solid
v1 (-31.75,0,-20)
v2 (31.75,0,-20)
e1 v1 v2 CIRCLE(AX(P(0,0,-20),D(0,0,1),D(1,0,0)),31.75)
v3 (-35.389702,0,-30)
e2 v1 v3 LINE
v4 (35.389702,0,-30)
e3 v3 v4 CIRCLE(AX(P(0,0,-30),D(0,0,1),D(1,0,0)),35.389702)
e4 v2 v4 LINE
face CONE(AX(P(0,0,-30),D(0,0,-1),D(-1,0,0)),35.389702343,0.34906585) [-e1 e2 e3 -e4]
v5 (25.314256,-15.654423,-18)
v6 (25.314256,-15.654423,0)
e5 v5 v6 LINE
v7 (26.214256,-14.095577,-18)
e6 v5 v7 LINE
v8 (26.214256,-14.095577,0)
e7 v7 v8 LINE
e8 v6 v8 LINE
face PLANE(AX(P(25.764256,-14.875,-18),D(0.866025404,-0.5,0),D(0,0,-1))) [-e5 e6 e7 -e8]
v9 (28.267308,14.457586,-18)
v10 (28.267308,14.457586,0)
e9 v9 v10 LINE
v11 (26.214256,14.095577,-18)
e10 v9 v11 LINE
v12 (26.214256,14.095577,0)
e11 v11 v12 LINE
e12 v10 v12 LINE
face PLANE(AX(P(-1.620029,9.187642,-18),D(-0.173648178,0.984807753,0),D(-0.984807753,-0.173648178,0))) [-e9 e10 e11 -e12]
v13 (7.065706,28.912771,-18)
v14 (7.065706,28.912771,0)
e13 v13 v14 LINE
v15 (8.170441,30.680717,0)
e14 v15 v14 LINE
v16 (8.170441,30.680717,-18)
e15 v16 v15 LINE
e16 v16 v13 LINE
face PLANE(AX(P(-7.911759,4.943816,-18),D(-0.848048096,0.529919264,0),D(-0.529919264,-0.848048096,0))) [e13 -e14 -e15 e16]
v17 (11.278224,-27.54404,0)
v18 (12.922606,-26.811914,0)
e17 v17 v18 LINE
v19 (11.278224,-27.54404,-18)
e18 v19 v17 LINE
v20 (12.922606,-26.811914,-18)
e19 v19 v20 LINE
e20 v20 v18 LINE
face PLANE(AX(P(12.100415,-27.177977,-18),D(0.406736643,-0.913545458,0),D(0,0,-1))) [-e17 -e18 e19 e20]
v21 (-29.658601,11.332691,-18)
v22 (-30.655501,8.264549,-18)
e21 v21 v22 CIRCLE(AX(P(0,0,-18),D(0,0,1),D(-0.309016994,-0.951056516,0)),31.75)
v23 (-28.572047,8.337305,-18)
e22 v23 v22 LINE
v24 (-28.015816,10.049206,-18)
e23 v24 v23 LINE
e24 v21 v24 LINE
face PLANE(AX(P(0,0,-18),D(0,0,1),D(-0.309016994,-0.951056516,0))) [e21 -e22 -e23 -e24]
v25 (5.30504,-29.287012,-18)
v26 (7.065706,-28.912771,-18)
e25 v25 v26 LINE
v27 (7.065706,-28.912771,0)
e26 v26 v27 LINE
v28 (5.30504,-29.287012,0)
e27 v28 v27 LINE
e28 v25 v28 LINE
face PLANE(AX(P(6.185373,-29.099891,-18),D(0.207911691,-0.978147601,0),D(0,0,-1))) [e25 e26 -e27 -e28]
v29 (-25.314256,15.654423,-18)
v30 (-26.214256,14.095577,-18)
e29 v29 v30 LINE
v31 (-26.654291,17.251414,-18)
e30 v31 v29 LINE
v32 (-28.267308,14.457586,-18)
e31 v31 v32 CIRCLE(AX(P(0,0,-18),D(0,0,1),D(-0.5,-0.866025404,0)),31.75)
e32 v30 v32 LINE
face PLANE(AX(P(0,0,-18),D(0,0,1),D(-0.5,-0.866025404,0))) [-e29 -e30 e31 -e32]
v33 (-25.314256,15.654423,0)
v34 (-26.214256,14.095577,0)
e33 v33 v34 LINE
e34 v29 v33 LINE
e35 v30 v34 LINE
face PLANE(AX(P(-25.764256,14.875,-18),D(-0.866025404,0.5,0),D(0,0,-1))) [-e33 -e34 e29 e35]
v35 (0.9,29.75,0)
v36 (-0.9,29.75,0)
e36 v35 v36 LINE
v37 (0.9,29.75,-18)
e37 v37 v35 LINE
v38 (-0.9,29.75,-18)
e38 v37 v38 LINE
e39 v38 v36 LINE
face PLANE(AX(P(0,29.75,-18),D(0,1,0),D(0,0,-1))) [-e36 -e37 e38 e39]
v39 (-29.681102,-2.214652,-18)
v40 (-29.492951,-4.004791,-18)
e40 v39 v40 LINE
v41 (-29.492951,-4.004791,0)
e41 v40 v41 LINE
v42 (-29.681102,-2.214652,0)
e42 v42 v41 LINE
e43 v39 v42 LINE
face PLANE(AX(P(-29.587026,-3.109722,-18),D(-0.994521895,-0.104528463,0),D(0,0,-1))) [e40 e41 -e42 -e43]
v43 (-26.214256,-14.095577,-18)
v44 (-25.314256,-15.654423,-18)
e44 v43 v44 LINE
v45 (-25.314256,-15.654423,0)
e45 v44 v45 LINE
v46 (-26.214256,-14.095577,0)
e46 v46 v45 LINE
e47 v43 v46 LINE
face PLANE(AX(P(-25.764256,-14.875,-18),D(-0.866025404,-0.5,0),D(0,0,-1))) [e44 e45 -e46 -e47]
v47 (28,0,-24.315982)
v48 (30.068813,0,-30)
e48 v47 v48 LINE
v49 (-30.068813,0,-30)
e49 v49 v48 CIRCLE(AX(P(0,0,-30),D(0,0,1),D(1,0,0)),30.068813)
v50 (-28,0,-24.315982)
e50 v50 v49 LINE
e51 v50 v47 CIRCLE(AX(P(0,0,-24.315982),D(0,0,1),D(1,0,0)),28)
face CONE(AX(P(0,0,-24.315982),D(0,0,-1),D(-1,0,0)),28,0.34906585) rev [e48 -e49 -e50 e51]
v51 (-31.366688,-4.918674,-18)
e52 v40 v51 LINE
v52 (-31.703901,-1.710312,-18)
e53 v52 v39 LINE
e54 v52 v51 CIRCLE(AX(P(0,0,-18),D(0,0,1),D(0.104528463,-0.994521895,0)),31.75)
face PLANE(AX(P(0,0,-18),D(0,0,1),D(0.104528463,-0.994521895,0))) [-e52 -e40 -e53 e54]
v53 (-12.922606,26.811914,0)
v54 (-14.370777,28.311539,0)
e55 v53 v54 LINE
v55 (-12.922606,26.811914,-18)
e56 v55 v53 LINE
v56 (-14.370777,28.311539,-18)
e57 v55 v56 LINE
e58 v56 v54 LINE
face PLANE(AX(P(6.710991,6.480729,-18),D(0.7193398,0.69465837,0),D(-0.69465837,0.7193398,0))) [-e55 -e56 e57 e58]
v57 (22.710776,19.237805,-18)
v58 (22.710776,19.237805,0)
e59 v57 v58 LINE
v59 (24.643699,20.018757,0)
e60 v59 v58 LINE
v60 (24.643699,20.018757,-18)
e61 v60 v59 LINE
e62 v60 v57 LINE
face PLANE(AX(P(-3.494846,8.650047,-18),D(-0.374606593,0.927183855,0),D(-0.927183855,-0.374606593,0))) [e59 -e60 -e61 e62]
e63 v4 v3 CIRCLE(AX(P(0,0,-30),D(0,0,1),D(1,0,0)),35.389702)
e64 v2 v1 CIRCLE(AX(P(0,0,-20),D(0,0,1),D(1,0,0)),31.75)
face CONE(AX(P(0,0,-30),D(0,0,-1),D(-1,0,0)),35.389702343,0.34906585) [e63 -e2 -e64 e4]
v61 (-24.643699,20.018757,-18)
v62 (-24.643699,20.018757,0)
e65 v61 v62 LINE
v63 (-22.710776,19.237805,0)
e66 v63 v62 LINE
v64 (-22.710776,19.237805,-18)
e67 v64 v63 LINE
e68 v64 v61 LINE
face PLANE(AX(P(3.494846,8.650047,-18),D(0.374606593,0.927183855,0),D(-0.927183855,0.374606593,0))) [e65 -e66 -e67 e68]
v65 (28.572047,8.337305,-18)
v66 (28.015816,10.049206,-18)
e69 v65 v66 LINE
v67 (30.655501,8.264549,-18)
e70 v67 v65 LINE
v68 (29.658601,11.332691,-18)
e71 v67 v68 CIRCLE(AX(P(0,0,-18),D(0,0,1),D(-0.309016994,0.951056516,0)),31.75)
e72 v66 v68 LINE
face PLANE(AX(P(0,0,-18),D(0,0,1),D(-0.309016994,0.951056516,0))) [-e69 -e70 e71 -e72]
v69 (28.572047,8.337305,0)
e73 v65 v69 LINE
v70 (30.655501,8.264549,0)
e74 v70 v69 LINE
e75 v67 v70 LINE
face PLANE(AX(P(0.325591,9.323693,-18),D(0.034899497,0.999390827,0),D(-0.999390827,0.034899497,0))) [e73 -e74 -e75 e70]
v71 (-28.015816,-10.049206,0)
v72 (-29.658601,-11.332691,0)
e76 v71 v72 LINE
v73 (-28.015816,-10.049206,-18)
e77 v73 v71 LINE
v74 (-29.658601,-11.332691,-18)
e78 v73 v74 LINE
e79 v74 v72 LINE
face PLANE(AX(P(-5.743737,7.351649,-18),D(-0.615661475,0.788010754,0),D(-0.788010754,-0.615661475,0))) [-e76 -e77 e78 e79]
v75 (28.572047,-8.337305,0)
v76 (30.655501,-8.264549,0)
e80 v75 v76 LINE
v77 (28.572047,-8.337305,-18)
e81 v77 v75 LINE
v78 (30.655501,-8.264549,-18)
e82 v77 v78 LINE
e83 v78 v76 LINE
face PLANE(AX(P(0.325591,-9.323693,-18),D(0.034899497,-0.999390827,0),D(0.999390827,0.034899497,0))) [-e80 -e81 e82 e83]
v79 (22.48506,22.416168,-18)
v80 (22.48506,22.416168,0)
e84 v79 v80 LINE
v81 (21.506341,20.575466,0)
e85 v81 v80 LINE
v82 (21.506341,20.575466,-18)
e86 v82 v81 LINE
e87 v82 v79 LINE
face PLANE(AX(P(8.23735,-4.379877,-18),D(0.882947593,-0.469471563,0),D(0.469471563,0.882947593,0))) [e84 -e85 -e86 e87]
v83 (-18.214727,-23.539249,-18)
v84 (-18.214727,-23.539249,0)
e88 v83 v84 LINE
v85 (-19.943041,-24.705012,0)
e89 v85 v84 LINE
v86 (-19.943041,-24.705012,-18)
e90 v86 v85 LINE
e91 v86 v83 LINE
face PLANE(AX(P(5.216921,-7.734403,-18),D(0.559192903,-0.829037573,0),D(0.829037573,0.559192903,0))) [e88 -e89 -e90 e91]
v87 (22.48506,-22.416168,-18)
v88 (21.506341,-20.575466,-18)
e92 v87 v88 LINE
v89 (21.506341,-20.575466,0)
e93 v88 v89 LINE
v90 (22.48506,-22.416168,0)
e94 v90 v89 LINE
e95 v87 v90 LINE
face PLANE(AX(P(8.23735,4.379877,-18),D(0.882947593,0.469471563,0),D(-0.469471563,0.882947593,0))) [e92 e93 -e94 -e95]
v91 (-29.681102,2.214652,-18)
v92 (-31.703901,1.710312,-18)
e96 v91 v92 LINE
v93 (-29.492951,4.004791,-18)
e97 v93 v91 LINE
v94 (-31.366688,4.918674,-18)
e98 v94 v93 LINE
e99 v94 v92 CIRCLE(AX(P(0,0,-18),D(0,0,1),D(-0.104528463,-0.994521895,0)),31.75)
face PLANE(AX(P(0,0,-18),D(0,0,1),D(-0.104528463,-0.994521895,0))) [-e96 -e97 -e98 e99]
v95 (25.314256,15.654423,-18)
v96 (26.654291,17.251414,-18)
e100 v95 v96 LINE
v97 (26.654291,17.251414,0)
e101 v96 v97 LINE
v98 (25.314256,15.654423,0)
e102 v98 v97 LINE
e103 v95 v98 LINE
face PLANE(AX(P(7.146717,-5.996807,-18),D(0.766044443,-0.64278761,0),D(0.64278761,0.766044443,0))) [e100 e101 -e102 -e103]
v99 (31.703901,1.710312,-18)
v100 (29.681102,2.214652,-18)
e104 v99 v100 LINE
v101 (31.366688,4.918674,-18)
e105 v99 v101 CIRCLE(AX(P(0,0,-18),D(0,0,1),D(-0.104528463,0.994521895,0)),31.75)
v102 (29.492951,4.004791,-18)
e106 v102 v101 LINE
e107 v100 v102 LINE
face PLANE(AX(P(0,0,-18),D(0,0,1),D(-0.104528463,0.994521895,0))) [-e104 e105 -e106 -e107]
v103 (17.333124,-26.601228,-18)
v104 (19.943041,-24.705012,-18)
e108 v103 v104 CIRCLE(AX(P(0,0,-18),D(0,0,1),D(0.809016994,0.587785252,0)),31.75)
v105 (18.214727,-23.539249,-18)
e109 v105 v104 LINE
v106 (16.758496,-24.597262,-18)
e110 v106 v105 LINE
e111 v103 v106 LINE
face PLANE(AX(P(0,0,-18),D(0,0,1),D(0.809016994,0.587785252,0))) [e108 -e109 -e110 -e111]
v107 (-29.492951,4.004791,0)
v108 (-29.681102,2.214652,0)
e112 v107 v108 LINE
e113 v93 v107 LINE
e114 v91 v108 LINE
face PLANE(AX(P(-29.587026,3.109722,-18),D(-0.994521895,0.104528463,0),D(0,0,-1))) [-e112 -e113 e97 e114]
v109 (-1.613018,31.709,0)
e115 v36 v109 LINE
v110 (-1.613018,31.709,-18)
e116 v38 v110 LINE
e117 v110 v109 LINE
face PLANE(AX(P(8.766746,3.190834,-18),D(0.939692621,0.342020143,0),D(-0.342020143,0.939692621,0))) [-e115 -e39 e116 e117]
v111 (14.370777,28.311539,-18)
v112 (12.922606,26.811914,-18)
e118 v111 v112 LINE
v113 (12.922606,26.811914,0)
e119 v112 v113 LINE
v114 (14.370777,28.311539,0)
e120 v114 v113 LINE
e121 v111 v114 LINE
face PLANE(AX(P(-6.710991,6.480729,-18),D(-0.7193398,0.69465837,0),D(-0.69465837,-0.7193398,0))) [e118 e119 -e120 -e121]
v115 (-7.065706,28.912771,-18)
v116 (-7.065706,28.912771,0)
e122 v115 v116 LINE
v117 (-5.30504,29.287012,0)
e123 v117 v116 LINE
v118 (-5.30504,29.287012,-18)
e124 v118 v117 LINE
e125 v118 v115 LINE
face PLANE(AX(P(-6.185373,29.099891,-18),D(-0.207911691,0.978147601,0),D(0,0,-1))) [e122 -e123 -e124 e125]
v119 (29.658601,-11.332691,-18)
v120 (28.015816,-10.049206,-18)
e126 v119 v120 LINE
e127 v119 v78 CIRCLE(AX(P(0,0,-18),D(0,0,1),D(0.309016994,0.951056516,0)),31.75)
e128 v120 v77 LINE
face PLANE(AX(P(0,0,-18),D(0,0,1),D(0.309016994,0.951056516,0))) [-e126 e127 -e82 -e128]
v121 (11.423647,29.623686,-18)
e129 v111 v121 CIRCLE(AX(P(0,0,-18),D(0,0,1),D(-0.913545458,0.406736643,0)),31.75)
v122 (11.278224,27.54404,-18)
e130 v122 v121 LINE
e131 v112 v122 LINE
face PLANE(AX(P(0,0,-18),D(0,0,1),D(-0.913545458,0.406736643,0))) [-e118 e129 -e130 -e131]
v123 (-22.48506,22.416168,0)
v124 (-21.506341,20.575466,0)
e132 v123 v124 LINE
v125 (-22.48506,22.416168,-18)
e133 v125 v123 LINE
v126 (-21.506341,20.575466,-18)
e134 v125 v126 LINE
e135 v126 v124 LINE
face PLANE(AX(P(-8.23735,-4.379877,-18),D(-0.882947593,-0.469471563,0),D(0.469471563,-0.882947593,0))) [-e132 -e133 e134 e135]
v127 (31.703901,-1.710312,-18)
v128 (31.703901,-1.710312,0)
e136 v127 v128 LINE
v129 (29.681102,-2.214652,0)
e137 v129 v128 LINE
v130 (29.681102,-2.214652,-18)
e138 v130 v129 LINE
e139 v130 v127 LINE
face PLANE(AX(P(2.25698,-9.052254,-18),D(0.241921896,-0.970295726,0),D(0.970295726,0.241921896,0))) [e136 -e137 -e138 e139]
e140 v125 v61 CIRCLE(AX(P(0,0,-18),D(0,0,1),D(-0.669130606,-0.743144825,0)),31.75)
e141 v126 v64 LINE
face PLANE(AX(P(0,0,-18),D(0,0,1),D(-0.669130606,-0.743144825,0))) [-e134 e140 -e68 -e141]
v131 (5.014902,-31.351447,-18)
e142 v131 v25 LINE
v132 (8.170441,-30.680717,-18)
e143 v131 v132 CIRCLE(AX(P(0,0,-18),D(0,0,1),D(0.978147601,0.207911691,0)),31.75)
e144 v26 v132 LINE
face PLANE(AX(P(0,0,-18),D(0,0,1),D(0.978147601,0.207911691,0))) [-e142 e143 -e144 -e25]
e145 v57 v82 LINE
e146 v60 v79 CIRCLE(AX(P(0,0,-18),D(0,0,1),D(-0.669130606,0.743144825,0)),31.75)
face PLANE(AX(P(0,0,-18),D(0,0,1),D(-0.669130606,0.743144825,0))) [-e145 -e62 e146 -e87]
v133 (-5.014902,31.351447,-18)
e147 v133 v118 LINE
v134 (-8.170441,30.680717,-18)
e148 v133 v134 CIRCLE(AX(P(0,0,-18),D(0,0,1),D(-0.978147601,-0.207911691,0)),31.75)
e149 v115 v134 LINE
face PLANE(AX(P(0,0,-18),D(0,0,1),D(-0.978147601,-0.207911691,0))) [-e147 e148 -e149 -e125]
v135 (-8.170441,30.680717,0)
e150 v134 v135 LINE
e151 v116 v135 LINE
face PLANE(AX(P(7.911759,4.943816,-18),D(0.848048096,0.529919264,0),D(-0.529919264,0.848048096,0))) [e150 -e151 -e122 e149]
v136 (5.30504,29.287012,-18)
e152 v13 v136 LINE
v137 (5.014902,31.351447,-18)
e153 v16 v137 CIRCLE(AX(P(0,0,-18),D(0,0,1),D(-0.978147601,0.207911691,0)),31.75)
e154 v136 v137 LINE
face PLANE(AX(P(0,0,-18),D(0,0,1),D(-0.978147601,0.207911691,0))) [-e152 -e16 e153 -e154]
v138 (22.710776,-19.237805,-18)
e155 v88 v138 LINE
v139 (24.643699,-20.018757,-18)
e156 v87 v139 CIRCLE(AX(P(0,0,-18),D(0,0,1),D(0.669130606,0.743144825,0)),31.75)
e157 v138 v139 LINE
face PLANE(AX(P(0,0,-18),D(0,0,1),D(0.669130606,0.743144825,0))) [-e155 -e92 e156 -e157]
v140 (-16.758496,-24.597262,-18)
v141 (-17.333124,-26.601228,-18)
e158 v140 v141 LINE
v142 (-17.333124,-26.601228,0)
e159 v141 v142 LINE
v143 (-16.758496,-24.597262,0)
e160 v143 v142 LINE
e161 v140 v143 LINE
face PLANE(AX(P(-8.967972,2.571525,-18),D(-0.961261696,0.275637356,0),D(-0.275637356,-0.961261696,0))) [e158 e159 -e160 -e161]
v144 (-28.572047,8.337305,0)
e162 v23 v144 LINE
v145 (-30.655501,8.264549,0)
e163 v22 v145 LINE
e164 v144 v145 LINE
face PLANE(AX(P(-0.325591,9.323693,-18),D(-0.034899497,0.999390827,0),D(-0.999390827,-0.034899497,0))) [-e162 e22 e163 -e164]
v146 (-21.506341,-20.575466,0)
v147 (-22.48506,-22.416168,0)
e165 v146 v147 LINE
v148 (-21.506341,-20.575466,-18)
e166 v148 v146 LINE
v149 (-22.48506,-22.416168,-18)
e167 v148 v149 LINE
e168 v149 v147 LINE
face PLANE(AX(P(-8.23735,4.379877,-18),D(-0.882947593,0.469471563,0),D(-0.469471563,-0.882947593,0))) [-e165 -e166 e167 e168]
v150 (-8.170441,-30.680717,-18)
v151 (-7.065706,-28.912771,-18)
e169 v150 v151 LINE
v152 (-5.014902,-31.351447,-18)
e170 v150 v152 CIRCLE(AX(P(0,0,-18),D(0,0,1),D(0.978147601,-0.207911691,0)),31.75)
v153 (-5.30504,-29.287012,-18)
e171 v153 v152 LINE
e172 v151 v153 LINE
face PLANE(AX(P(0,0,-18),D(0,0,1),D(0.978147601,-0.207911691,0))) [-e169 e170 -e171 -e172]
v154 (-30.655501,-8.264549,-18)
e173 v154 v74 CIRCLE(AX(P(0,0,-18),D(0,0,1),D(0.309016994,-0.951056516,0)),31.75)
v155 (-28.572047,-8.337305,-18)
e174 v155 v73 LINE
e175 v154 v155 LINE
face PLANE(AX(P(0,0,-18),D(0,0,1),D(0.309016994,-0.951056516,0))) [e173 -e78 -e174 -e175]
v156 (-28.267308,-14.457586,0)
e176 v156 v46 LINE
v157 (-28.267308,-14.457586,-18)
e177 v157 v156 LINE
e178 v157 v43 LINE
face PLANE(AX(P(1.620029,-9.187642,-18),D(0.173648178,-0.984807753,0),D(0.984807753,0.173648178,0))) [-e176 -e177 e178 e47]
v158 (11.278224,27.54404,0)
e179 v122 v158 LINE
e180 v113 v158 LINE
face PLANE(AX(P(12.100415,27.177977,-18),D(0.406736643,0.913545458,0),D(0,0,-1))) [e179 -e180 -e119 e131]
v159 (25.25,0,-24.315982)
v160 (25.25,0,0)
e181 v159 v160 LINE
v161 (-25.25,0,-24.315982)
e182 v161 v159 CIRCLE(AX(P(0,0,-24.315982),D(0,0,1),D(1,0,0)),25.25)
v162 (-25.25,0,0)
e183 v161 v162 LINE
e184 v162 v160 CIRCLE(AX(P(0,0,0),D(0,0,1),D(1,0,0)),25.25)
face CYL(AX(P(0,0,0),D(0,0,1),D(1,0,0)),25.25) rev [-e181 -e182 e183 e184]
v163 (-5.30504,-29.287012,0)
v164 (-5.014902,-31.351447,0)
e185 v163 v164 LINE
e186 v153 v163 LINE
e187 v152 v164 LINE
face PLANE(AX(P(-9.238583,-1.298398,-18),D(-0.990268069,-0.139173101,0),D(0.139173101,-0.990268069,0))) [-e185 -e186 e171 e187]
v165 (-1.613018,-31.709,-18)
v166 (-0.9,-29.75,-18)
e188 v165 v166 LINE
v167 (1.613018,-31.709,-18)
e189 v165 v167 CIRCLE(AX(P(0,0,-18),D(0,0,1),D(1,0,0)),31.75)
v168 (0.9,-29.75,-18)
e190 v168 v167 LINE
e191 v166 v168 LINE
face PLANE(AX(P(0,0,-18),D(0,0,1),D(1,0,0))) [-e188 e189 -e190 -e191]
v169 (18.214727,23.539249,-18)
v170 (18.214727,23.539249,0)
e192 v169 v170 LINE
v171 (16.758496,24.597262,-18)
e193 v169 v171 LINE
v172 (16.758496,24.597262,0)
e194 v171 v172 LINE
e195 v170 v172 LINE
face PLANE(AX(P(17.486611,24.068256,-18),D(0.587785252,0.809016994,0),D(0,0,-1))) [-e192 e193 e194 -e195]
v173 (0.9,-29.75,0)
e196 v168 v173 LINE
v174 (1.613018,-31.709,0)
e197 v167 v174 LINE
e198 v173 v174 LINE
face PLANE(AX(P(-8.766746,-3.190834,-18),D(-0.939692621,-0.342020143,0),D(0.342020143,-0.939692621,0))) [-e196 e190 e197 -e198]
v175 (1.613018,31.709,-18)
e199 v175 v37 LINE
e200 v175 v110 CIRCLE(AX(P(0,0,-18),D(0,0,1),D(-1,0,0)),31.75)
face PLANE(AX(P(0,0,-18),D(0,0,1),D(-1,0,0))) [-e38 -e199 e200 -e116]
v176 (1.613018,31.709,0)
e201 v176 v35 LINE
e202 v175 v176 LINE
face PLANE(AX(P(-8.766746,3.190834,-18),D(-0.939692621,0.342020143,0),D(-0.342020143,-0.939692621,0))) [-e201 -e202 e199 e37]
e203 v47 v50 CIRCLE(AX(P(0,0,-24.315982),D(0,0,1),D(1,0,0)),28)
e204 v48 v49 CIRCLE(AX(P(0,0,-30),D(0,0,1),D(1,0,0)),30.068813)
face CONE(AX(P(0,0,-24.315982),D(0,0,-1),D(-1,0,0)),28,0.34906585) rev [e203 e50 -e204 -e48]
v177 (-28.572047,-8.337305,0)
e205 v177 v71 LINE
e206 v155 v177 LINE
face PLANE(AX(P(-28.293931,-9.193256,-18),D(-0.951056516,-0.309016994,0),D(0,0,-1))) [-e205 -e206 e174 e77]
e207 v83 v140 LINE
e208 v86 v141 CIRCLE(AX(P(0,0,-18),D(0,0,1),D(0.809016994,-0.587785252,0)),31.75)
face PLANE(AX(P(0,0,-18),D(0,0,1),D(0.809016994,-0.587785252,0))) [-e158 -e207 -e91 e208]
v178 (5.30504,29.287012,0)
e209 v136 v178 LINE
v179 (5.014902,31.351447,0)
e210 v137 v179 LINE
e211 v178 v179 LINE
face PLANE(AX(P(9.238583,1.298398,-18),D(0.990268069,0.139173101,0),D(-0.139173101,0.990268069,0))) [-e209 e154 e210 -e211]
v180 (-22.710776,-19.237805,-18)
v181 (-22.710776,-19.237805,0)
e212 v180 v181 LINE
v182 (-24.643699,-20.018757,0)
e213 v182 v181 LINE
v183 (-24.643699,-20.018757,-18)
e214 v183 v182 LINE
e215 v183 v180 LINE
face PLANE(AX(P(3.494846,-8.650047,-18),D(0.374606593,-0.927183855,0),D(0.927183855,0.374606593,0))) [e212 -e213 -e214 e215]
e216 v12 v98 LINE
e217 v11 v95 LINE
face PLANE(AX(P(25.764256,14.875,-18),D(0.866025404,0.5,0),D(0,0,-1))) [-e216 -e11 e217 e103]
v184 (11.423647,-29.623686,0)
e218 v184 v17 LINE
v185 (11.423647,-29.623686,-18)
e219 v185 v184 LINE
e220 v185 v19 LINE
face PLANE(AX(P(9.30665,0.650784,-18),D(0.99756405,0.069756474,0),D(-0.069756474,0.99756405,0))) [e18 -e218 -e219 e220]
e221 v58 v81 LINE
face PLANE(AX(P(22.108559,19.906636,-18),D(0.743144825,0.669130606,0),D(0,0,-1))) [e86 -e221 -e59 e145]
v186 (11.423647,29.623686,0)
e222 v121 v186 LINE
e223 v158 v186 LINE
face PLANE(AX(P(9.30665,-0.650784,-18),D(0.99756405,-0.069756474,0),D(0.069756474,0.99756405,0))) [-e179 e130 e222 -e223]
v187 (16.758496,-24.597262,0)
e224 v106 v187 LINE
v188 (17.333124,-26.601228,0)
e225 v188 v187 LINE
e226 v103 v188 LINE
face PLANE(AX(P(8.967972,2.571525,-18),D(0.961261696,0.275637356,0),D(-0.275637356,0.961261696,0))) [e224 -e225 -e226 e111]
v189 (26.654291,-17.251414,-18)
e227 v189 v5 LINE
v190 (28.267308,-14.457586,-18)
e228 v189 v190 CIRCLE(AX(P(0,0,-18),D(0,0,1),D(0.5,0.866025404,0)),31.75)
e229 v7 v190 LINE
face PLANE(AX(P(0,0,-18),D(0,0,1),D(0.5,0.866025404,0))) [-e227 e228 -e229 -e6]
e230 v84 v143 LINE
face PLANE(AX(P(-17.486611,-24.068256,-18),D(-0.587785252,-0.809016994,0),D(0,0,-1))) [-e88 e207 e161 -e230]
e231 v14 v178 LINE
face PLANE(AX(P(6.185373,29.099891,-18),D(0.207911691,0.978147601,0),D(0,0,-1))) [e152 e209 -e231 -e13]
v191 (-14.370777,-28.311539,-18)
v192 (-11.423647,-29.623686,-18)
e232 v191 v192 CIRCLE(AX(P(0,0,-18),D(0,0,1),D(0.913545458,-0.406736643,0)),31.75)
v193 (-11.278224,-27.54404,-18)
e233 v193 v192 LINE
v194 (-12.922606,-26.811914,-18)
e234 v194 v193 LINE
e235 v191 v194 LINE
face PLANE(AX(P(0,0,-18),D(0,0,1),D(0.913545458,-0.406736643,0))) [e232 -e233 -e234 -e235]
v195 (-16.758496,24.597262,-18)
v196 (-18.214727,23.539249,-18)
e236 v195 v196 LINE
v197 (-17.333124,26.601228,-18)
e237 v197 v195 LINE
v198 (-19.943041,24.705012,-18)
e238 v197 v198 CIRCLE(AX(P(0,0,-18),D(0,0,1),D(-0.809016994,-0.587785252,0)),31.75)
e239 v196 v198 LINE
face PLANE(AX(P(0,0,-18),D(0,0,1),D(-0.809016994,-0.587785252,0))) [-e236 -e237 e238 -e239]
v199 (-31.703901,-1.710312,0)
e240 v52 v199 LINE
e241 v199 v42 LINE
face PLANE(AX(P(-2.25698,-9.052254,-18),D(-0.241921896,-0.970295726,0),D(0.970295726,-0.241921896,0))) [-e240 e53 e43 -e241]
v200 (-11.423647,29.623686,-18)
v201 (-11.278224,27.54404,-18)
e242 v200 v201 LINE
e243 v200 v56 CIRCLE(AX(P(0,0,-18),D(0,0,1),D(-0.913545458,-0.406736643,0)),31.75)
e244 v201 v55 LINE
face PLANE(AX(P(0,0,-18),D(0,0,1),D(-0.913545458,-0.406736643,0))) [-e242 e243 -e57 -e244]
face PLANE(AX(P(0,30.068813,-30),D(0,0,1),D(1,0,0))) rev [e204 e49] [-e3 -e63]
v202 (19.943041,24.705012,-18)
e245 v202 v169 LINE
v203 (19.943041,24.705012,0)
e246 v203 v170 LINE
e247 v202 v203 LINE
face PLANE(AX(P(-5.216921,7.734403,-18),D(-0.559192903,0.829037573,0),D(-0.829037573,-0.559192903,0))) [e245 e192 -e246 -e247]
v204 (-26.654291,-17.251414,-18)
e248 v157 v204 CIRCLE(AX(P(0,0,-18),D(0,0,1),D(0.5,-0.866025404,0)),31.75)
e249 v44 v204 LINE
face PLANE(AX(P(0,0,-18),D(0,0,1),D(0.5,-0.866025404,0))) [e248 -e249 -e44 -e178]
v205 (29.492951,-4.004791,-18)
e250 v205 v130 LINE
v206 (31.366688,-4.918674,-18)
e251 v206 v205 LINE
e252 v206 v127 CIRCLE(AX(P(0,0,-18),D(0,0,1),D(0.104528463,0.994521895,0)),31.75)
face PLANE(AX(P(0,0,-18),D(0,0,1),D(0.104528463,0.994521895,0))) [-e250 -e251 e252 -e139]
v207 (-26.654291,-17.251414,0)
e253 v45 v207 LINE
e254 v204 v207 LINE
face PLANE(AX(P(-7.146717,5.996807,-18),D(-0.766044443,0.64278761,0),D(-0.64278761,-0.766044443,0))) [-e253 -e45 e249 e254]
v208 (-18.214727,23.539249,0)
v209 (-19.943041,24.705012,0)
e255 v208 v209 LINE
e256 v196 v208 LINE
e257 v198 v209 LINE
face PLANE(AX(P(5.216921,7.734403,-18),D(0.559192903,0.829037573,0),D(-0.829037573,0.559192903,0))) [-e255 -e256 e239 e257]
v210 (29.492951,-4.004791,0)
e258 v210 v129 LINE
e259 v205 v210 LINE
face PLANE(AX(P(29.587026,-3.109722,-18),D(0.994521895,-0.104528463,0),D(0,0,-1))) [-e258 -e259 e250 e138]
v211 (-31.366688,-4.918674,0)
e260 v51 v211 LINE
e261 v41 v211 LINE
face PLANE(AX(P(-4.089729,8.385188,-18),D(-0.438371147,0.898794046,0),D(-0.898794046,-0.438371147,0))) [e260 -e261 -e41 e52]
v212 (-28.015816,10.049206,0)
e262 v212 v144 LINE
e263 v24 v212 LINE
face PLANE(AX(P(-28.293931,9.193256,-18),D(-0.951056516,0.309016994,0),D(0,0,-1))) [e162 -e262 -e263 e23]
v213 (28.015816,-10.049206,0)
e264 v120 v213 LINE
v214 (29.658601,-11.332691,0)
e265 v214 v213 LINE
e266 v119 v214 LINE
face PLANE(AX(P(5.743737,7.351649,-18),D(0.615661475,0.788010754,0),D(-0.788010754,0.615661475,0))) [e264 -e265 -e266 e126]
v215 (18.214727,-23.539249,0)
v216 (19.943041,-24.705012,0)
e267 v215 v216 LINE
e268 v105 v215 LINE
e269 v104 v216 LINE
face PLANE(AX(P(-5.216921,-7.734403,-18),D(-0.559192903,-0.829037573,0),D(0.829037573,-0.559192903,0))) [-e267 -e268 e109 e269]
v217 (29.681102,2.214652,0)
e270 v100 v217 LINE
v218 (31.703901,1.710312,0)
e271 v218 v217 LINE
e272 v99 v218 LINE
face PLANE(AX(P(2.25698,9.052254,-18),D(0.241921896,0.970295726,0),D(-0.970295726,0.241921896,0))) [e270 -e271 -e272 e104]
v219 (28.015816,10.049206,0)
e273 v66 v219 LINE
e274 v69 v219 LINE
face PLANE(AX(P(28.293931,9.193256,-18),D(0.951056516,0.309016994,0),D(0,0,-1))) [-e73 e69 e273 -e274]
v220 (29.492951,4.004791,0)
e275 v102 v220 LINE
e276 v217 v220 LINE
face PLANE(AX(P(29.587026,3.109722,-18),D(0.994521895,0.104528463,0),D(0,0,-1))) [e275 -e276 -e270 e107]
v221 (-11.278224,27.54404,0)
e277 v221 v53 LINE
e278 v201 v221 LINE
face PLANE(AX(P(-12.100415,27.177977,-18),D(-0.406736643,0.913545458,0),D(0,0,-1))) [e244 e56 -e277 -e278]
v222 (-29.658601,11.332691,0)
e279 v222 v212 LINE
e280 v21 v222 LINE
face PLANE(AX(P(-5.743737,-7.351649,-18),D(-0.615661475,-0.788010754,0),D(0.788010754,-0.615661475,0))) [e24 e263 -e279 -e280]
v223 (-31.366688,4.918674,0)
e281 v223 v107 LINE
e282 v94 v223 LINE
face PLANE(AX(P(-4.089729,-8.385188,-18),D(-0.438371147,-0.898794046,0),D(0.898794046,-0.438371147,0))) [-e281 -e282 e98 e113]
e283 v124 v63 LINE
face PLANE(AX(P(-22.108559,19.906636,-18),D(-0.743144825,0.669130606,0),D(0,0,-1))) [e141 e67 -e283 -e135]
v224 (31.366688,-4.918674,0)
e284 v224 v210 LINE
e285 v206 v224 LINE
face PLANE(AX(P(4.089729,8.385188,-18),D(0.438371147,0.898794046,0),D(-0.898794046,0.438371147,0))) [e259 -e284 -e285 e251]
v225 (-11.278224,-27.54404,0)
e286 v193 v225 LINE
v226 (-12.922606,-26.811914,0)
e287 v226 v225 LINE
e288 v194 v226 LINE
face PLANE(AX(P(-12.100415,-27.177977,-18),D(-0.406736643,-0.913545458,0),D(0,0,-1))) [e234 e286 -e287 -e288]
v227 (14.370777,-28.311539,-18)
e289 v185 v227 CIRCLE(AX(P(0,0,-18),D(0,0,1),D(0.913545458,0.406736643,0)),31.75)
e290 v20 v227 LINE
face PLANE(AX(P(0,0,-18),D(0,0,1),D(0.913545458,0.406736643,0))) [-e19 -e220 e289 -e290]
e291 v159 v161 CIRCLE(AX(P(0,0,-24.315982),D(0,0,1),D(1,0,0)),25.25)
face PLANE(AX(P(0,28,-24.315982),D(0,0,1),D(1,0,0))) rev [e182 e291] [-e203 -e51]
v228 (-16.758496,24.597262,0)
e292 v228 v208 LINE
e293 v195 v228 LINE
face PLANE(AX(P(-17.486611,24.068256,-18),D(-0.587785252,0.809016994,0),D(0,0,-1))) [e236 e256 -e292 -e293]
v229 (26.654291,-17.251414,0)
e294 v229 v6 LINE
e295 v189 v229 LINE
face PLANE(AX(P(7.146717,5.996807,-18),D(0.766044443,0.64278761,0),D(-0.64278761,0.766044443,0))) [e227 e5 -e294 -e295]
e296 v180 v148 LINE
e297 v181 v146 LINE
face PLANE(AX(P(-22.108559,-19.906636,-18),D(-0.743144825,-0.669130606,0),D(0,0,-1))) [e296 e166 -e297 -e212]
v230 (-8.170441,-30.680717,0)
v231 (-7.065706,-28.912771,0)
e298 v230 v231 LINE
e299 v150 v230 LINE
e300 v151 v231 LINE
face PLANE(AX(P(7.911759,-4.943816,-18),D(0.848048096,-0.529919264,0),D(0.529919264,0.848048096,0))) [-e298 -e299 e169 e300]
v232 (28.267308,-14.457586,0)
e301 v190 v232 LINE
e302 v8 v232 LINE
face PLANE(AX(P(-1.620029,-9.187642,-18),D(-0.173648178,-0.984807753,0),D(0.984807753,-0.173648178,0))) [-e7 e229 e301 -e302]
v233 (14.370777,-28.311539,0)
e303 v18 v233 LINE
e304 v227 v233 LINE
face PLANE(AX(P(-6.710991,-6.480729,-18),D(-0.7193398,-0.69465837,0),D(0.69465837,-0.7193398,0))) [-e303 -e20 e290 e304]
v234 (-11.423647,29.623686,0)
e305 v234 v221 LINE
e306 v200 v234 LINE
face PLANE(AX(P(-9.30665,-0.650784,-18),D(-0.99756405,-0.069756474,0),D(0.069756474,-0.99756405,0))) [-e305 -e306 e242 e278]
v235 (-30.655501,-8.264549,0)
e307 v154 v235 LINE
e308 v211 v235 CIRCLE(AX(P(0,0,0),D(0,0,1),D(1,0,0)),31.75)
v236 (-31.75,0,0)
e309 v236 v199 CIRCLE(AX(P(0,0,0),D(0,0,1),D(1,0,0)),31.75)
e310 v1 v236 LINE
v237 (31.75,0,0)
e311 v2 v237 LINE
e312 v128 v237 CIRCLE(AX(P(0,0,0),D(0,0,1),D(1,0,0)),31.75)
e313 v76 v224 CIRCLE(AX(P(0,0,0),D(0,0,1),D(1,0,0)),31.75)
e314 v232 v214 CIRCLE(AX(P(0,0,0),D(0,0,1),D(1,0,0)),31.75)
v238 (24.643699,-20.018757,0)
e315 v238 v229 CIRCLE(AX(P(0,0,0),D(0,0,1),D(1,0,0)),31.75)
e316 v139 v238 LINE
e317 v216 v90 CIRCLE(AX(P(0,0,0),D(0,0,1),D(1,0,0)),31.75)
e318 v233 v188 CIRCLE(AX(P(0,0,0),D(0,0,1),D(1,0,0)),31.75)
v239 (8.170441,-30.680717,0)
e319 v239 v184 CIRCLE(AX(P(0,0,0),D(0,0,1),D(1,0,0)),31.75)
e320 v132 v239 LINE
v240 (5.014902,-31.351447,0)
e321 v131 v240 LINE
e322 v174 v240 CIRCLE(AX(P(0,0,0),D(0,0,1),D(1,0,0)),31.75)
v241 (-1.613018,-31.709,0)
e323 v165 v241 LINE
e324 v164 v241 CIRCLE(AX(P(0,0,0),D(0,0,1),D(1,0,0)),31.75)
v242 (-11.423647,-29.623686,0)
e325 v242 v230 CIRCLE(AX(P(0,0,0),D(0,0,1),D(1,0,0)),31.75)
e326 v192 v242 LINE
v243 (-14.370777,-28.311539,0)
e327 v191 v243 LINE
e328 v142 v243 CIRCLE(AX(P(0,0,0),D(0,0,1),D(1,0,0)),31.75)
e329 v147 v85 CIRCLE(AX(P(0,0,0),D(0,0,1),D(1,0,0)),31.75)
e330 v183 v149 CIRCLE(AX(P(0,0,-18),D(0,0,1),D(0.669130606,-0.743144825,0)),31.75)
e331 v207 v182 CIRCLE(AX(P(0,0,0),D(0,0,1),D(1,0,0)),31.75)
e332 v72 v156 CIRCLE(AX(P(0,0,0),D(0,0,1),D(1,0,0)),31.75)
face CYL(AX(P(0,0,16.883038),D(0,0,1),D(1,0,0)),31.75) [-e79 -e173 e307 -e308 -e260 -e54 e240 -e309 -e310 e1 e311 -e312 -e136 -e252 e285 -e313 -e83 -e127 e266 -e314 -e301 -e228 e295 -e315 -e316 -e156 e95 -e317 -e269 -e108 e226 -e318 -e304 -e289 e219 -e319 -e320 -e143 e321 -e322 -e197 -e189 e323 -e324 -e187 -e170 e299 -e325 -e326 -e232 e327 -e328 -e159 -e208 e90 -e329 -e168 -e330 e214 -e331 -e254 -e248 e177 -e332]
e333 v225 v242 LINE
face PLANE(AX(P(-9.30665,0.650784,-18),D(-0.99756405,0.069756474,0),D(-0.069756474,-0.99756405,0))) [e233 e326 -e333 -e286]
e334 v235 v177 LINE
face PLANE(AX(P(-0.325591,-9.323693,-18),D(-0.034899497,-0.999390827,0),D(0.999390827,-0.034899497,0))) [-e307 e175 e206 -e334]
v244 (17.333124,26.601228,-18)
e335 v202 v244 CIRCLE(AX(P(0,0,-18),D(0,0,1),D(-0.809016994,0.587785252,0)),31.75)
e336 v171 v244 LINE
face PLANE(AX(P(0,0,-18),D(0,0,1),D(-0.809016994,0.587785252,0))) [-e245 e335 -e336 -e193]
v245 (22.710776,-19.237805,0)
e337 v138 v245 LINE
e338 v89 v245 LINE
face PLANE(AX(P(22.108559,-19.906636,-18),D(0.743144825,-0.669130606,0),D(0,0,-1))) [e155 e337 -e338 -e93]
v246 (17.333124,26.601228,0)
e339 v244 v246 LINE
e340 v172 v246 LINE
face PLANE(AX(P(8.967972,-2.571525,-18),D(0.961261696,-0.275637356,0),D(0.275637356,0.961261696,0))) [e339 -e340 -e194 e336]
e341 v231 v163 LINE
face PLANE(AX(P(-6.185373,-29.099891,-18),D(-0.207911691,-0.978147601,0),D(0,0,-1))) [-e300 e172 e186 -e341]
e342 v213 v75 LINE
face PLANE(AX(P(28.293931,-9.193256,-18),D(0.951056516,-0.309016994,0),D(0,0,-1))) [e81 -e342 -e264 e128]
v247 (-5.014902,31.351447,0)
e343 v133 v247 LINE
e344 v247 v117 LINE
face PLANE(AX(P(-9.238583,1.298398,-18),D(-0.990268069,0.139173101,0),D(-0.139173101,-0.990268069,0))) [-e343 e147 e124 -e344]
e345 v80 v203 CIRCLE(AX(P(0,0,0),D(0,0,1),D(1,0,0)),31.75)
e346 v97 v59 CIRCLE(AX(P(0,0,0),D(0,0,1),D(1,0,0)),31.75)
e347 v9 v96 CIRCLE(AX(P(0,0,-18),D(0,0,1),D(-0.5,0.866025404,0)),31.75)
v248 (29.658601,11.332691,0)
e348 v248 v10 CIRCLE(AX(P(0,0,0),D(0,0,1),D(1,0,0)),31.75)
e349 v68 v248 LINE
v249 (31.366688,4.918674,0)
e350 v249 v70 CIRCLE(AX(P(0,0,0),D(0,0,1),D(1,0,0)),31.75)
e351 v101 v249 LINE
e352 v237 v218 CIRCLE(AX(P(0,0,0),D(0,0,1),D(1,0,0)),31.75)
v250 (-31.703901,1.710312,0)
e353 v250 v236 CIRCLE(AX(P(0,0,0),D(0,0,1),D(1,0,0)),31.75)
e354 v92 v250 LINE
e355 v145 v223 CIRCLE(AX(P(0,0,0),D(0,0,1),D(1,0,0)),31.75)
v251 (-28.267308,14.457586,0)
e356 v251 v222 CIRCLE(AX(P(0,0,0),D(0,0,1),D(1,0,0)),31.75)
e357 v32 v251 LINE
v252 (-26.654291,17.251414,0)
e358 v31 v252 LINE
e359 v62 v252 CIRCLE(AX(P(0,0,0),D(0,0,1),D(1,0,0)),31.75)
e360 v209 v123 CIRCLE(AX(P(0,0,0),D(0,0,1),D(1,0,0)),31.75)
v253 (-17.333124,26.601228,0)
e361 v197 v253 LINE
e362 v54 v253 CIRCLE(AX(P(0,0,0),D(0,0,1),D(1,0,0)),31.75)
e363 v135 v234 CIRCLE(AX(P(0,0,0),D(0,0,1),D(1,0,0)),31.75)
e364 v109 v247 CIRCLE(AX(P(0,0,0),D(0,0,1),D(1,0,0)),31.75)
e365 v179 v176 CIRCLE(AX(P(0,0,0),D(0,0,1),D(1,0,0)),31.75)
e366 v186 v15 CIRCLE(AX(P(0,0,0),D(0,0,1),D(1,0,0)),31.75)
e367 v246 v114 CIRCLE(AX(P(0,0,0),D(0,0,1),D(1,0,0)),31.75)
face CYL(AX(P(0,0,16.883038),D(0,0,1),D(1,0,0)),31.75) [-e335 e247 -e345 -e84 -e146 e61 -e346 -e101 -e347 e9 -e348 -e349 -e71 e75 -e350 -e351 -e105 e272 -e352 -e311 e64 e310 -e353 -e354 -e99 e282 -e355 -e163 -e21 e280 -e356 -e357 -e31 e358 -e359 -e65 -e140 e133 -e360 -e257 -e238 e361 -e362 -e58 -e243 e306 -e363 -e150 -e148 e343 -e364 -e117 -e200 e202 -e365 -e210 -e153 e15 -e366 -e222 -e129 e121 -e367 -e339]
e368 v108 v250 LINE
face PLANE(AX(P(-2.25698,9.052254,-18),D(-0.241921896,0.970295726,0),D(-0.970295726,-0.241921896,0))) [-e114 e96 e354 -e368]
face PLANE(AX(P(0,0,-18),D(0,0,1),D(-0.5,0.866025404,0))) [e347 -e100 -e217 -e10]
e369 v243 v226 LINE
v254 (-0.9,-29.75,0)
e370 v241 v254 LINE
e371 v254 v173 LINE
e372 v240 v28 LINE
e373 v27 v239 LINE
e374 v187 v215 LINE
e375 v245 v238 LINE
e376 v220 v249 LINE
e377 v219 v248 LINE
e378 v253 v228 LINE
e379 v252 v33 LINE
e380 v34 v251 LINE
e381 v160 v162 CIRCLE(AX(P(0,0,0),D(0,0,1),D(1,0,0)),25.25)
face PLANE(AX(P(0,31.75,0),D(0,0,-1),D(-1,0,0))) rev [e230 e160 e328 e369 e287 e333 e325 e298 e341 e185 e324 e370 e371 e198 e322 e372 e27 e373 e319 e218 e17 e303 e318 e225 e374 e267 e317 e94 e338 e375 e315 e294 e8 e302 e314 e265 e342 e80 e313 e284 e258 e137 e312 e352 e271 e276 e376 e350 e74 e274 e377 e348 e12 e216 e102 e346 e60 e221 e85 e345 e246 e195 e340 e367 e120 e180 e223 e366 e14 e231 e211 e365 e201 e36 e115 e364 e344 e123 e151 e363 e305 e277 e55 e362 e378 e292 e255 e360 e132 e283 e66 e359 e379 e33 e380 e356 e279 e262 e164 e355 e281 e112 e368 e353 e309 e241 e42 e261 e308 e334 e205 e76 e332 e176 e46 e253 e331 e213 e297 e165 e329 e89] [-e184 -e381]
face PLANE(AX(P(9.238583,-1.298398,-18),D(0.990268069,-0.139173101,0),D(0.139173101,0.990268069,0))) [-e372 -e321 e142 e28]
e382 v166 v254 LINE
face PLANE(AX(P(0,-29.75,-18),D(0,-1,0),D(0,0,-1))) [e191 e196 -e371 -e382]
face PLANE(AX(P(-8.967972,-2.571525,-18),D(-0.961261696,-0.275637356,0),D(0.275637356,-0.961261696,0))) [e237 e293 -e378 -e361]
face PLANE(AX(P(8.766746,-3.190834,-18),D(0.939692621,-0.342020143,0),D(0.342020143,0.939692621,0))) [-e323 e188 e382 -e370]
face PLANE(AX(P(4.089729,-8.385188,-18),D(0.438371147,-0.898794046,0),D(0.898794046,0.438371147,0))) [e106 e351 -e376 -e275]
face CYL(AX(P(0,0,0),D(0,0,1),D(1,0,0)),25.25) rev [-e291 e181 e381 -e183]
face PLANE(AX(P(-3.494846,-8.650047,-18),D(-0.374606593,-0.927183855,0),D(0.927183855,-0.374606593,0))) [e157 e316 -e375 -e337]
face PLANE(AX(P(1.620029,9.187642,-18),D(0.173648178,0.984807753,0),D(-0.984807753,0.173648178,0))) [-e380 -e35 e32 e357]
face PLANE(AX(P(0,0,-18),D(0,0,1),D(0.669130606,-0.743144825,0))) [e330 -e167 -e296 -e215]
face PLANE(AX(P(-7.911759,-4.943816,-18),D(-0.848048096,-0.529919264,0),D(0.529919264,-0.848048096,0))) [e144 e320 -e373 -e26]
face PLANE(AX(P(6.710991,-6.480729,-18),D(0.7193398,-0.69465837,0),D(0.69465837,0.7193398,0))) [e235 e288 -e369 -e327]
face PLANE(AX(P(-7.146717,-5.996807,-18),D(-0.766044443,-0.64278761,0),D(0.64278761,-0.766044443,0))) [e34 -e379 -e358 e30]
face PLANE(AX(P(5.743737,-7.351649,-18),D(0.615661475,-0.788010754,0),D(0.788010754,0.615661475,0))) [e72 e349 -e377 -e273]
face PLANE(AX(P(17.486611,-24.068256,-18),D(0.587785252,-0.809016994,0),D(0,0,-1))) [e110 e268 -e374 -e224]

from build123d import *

# Parameters (mm, degrees)
M56_TAPPED_HOLE1_D     = 50.5
M56_TAPPED_HOLE1_DEPTH = 128.5
M56_TAPPED_HOLE1_TIP   = 15.17173063
CUT_EXTRUDE1_DEPTH     = 18
CIRPATTERN1_COUNT      = 30


with BuildPart() as part:
    # Sketch1 → Revolve1 (revolve)
    with BuildSketch(Plane(origin=(0, 0, 0), x_dir=(0, 0, -1), z_dir=(1, 0, 0)), mode=Mode.PRIVATE) as revolve1_sk:
        Polygon((0, 31.75), (0, 0), (24.315981678, 0), (24.315981678, 28), (30, 30.06881348), (30, 35.389702343), (20, 31.75), align=None)
    revolve(revolve1_sk.sketch.rotate(Axis((0, 0, 16.883037514), (0, 0, -1)), 90), axis=Axis((0, 0, 16.883037514), (0, 0, -1)))

    # M56 Tapped Hole1
    with Locations(Plane.XY):
        with Locations((0, 0)):
            Hole(M56_TAPPED_HOLE1_D / 2, depth=M56_TAPPED_HOLE1_DEPTH)
            with Locations((0, 0, -(M56_TAPPED_HOLE1_DEPTH + M56_TAPPED_HOLE1_TIP / 2))):  # 118° drill point
                Cone(0, M56_TAPPED_HOLE1_D / 2, M56_TAPPED_HOLE1_TIP, mode=Mode.SUBTRACT)

    # Sketch6 → Cut-Extrude1 (cut)
    with BuildSketch(Plane.XY):
        with BuildLine():
            Line((0, -31.75), (0, -29.75))
            Line((0, -29.75), (-0.9, -29.75))
            Line((-0.9, -29.75), (-1.613017649, -31.708999891))
            ThreePointArc((-1.613017649, -31.708999891), (-0.80676932, -31.739748318), (0, -31.75))
        make_face()
        with BuildLine():
            Line((0.9, -29.75), (0, -29.75))
            Line((0, -29.75), (0, -31.75))
            ThreePointArc((0, -31.75), (0.80676932, -31.739748318), (1.613017649, -31.708999891))
            Line((1.613017649, -31.708999891), (0.9, -29.75))
        make_face()
    cut_extrude1 = extrude(amount=-CUT_EXTRUDE1_DEPTH, mode=Mode.SUBTRACT)

    # CirPattern1: Cut-Extrude1 ×30 about axis
    cirpattern1_axis = Axis((0, 0, 0), (0, 0, 1))
    for i in range(1, CIRPATTERN1_COUNT):
        add(cut_extrude1.rotate(cirpattern1_axis, i * 360 / CIRPATTERN1_COUNT), mode=Mode.SUBTRACT)


solid = part.part
